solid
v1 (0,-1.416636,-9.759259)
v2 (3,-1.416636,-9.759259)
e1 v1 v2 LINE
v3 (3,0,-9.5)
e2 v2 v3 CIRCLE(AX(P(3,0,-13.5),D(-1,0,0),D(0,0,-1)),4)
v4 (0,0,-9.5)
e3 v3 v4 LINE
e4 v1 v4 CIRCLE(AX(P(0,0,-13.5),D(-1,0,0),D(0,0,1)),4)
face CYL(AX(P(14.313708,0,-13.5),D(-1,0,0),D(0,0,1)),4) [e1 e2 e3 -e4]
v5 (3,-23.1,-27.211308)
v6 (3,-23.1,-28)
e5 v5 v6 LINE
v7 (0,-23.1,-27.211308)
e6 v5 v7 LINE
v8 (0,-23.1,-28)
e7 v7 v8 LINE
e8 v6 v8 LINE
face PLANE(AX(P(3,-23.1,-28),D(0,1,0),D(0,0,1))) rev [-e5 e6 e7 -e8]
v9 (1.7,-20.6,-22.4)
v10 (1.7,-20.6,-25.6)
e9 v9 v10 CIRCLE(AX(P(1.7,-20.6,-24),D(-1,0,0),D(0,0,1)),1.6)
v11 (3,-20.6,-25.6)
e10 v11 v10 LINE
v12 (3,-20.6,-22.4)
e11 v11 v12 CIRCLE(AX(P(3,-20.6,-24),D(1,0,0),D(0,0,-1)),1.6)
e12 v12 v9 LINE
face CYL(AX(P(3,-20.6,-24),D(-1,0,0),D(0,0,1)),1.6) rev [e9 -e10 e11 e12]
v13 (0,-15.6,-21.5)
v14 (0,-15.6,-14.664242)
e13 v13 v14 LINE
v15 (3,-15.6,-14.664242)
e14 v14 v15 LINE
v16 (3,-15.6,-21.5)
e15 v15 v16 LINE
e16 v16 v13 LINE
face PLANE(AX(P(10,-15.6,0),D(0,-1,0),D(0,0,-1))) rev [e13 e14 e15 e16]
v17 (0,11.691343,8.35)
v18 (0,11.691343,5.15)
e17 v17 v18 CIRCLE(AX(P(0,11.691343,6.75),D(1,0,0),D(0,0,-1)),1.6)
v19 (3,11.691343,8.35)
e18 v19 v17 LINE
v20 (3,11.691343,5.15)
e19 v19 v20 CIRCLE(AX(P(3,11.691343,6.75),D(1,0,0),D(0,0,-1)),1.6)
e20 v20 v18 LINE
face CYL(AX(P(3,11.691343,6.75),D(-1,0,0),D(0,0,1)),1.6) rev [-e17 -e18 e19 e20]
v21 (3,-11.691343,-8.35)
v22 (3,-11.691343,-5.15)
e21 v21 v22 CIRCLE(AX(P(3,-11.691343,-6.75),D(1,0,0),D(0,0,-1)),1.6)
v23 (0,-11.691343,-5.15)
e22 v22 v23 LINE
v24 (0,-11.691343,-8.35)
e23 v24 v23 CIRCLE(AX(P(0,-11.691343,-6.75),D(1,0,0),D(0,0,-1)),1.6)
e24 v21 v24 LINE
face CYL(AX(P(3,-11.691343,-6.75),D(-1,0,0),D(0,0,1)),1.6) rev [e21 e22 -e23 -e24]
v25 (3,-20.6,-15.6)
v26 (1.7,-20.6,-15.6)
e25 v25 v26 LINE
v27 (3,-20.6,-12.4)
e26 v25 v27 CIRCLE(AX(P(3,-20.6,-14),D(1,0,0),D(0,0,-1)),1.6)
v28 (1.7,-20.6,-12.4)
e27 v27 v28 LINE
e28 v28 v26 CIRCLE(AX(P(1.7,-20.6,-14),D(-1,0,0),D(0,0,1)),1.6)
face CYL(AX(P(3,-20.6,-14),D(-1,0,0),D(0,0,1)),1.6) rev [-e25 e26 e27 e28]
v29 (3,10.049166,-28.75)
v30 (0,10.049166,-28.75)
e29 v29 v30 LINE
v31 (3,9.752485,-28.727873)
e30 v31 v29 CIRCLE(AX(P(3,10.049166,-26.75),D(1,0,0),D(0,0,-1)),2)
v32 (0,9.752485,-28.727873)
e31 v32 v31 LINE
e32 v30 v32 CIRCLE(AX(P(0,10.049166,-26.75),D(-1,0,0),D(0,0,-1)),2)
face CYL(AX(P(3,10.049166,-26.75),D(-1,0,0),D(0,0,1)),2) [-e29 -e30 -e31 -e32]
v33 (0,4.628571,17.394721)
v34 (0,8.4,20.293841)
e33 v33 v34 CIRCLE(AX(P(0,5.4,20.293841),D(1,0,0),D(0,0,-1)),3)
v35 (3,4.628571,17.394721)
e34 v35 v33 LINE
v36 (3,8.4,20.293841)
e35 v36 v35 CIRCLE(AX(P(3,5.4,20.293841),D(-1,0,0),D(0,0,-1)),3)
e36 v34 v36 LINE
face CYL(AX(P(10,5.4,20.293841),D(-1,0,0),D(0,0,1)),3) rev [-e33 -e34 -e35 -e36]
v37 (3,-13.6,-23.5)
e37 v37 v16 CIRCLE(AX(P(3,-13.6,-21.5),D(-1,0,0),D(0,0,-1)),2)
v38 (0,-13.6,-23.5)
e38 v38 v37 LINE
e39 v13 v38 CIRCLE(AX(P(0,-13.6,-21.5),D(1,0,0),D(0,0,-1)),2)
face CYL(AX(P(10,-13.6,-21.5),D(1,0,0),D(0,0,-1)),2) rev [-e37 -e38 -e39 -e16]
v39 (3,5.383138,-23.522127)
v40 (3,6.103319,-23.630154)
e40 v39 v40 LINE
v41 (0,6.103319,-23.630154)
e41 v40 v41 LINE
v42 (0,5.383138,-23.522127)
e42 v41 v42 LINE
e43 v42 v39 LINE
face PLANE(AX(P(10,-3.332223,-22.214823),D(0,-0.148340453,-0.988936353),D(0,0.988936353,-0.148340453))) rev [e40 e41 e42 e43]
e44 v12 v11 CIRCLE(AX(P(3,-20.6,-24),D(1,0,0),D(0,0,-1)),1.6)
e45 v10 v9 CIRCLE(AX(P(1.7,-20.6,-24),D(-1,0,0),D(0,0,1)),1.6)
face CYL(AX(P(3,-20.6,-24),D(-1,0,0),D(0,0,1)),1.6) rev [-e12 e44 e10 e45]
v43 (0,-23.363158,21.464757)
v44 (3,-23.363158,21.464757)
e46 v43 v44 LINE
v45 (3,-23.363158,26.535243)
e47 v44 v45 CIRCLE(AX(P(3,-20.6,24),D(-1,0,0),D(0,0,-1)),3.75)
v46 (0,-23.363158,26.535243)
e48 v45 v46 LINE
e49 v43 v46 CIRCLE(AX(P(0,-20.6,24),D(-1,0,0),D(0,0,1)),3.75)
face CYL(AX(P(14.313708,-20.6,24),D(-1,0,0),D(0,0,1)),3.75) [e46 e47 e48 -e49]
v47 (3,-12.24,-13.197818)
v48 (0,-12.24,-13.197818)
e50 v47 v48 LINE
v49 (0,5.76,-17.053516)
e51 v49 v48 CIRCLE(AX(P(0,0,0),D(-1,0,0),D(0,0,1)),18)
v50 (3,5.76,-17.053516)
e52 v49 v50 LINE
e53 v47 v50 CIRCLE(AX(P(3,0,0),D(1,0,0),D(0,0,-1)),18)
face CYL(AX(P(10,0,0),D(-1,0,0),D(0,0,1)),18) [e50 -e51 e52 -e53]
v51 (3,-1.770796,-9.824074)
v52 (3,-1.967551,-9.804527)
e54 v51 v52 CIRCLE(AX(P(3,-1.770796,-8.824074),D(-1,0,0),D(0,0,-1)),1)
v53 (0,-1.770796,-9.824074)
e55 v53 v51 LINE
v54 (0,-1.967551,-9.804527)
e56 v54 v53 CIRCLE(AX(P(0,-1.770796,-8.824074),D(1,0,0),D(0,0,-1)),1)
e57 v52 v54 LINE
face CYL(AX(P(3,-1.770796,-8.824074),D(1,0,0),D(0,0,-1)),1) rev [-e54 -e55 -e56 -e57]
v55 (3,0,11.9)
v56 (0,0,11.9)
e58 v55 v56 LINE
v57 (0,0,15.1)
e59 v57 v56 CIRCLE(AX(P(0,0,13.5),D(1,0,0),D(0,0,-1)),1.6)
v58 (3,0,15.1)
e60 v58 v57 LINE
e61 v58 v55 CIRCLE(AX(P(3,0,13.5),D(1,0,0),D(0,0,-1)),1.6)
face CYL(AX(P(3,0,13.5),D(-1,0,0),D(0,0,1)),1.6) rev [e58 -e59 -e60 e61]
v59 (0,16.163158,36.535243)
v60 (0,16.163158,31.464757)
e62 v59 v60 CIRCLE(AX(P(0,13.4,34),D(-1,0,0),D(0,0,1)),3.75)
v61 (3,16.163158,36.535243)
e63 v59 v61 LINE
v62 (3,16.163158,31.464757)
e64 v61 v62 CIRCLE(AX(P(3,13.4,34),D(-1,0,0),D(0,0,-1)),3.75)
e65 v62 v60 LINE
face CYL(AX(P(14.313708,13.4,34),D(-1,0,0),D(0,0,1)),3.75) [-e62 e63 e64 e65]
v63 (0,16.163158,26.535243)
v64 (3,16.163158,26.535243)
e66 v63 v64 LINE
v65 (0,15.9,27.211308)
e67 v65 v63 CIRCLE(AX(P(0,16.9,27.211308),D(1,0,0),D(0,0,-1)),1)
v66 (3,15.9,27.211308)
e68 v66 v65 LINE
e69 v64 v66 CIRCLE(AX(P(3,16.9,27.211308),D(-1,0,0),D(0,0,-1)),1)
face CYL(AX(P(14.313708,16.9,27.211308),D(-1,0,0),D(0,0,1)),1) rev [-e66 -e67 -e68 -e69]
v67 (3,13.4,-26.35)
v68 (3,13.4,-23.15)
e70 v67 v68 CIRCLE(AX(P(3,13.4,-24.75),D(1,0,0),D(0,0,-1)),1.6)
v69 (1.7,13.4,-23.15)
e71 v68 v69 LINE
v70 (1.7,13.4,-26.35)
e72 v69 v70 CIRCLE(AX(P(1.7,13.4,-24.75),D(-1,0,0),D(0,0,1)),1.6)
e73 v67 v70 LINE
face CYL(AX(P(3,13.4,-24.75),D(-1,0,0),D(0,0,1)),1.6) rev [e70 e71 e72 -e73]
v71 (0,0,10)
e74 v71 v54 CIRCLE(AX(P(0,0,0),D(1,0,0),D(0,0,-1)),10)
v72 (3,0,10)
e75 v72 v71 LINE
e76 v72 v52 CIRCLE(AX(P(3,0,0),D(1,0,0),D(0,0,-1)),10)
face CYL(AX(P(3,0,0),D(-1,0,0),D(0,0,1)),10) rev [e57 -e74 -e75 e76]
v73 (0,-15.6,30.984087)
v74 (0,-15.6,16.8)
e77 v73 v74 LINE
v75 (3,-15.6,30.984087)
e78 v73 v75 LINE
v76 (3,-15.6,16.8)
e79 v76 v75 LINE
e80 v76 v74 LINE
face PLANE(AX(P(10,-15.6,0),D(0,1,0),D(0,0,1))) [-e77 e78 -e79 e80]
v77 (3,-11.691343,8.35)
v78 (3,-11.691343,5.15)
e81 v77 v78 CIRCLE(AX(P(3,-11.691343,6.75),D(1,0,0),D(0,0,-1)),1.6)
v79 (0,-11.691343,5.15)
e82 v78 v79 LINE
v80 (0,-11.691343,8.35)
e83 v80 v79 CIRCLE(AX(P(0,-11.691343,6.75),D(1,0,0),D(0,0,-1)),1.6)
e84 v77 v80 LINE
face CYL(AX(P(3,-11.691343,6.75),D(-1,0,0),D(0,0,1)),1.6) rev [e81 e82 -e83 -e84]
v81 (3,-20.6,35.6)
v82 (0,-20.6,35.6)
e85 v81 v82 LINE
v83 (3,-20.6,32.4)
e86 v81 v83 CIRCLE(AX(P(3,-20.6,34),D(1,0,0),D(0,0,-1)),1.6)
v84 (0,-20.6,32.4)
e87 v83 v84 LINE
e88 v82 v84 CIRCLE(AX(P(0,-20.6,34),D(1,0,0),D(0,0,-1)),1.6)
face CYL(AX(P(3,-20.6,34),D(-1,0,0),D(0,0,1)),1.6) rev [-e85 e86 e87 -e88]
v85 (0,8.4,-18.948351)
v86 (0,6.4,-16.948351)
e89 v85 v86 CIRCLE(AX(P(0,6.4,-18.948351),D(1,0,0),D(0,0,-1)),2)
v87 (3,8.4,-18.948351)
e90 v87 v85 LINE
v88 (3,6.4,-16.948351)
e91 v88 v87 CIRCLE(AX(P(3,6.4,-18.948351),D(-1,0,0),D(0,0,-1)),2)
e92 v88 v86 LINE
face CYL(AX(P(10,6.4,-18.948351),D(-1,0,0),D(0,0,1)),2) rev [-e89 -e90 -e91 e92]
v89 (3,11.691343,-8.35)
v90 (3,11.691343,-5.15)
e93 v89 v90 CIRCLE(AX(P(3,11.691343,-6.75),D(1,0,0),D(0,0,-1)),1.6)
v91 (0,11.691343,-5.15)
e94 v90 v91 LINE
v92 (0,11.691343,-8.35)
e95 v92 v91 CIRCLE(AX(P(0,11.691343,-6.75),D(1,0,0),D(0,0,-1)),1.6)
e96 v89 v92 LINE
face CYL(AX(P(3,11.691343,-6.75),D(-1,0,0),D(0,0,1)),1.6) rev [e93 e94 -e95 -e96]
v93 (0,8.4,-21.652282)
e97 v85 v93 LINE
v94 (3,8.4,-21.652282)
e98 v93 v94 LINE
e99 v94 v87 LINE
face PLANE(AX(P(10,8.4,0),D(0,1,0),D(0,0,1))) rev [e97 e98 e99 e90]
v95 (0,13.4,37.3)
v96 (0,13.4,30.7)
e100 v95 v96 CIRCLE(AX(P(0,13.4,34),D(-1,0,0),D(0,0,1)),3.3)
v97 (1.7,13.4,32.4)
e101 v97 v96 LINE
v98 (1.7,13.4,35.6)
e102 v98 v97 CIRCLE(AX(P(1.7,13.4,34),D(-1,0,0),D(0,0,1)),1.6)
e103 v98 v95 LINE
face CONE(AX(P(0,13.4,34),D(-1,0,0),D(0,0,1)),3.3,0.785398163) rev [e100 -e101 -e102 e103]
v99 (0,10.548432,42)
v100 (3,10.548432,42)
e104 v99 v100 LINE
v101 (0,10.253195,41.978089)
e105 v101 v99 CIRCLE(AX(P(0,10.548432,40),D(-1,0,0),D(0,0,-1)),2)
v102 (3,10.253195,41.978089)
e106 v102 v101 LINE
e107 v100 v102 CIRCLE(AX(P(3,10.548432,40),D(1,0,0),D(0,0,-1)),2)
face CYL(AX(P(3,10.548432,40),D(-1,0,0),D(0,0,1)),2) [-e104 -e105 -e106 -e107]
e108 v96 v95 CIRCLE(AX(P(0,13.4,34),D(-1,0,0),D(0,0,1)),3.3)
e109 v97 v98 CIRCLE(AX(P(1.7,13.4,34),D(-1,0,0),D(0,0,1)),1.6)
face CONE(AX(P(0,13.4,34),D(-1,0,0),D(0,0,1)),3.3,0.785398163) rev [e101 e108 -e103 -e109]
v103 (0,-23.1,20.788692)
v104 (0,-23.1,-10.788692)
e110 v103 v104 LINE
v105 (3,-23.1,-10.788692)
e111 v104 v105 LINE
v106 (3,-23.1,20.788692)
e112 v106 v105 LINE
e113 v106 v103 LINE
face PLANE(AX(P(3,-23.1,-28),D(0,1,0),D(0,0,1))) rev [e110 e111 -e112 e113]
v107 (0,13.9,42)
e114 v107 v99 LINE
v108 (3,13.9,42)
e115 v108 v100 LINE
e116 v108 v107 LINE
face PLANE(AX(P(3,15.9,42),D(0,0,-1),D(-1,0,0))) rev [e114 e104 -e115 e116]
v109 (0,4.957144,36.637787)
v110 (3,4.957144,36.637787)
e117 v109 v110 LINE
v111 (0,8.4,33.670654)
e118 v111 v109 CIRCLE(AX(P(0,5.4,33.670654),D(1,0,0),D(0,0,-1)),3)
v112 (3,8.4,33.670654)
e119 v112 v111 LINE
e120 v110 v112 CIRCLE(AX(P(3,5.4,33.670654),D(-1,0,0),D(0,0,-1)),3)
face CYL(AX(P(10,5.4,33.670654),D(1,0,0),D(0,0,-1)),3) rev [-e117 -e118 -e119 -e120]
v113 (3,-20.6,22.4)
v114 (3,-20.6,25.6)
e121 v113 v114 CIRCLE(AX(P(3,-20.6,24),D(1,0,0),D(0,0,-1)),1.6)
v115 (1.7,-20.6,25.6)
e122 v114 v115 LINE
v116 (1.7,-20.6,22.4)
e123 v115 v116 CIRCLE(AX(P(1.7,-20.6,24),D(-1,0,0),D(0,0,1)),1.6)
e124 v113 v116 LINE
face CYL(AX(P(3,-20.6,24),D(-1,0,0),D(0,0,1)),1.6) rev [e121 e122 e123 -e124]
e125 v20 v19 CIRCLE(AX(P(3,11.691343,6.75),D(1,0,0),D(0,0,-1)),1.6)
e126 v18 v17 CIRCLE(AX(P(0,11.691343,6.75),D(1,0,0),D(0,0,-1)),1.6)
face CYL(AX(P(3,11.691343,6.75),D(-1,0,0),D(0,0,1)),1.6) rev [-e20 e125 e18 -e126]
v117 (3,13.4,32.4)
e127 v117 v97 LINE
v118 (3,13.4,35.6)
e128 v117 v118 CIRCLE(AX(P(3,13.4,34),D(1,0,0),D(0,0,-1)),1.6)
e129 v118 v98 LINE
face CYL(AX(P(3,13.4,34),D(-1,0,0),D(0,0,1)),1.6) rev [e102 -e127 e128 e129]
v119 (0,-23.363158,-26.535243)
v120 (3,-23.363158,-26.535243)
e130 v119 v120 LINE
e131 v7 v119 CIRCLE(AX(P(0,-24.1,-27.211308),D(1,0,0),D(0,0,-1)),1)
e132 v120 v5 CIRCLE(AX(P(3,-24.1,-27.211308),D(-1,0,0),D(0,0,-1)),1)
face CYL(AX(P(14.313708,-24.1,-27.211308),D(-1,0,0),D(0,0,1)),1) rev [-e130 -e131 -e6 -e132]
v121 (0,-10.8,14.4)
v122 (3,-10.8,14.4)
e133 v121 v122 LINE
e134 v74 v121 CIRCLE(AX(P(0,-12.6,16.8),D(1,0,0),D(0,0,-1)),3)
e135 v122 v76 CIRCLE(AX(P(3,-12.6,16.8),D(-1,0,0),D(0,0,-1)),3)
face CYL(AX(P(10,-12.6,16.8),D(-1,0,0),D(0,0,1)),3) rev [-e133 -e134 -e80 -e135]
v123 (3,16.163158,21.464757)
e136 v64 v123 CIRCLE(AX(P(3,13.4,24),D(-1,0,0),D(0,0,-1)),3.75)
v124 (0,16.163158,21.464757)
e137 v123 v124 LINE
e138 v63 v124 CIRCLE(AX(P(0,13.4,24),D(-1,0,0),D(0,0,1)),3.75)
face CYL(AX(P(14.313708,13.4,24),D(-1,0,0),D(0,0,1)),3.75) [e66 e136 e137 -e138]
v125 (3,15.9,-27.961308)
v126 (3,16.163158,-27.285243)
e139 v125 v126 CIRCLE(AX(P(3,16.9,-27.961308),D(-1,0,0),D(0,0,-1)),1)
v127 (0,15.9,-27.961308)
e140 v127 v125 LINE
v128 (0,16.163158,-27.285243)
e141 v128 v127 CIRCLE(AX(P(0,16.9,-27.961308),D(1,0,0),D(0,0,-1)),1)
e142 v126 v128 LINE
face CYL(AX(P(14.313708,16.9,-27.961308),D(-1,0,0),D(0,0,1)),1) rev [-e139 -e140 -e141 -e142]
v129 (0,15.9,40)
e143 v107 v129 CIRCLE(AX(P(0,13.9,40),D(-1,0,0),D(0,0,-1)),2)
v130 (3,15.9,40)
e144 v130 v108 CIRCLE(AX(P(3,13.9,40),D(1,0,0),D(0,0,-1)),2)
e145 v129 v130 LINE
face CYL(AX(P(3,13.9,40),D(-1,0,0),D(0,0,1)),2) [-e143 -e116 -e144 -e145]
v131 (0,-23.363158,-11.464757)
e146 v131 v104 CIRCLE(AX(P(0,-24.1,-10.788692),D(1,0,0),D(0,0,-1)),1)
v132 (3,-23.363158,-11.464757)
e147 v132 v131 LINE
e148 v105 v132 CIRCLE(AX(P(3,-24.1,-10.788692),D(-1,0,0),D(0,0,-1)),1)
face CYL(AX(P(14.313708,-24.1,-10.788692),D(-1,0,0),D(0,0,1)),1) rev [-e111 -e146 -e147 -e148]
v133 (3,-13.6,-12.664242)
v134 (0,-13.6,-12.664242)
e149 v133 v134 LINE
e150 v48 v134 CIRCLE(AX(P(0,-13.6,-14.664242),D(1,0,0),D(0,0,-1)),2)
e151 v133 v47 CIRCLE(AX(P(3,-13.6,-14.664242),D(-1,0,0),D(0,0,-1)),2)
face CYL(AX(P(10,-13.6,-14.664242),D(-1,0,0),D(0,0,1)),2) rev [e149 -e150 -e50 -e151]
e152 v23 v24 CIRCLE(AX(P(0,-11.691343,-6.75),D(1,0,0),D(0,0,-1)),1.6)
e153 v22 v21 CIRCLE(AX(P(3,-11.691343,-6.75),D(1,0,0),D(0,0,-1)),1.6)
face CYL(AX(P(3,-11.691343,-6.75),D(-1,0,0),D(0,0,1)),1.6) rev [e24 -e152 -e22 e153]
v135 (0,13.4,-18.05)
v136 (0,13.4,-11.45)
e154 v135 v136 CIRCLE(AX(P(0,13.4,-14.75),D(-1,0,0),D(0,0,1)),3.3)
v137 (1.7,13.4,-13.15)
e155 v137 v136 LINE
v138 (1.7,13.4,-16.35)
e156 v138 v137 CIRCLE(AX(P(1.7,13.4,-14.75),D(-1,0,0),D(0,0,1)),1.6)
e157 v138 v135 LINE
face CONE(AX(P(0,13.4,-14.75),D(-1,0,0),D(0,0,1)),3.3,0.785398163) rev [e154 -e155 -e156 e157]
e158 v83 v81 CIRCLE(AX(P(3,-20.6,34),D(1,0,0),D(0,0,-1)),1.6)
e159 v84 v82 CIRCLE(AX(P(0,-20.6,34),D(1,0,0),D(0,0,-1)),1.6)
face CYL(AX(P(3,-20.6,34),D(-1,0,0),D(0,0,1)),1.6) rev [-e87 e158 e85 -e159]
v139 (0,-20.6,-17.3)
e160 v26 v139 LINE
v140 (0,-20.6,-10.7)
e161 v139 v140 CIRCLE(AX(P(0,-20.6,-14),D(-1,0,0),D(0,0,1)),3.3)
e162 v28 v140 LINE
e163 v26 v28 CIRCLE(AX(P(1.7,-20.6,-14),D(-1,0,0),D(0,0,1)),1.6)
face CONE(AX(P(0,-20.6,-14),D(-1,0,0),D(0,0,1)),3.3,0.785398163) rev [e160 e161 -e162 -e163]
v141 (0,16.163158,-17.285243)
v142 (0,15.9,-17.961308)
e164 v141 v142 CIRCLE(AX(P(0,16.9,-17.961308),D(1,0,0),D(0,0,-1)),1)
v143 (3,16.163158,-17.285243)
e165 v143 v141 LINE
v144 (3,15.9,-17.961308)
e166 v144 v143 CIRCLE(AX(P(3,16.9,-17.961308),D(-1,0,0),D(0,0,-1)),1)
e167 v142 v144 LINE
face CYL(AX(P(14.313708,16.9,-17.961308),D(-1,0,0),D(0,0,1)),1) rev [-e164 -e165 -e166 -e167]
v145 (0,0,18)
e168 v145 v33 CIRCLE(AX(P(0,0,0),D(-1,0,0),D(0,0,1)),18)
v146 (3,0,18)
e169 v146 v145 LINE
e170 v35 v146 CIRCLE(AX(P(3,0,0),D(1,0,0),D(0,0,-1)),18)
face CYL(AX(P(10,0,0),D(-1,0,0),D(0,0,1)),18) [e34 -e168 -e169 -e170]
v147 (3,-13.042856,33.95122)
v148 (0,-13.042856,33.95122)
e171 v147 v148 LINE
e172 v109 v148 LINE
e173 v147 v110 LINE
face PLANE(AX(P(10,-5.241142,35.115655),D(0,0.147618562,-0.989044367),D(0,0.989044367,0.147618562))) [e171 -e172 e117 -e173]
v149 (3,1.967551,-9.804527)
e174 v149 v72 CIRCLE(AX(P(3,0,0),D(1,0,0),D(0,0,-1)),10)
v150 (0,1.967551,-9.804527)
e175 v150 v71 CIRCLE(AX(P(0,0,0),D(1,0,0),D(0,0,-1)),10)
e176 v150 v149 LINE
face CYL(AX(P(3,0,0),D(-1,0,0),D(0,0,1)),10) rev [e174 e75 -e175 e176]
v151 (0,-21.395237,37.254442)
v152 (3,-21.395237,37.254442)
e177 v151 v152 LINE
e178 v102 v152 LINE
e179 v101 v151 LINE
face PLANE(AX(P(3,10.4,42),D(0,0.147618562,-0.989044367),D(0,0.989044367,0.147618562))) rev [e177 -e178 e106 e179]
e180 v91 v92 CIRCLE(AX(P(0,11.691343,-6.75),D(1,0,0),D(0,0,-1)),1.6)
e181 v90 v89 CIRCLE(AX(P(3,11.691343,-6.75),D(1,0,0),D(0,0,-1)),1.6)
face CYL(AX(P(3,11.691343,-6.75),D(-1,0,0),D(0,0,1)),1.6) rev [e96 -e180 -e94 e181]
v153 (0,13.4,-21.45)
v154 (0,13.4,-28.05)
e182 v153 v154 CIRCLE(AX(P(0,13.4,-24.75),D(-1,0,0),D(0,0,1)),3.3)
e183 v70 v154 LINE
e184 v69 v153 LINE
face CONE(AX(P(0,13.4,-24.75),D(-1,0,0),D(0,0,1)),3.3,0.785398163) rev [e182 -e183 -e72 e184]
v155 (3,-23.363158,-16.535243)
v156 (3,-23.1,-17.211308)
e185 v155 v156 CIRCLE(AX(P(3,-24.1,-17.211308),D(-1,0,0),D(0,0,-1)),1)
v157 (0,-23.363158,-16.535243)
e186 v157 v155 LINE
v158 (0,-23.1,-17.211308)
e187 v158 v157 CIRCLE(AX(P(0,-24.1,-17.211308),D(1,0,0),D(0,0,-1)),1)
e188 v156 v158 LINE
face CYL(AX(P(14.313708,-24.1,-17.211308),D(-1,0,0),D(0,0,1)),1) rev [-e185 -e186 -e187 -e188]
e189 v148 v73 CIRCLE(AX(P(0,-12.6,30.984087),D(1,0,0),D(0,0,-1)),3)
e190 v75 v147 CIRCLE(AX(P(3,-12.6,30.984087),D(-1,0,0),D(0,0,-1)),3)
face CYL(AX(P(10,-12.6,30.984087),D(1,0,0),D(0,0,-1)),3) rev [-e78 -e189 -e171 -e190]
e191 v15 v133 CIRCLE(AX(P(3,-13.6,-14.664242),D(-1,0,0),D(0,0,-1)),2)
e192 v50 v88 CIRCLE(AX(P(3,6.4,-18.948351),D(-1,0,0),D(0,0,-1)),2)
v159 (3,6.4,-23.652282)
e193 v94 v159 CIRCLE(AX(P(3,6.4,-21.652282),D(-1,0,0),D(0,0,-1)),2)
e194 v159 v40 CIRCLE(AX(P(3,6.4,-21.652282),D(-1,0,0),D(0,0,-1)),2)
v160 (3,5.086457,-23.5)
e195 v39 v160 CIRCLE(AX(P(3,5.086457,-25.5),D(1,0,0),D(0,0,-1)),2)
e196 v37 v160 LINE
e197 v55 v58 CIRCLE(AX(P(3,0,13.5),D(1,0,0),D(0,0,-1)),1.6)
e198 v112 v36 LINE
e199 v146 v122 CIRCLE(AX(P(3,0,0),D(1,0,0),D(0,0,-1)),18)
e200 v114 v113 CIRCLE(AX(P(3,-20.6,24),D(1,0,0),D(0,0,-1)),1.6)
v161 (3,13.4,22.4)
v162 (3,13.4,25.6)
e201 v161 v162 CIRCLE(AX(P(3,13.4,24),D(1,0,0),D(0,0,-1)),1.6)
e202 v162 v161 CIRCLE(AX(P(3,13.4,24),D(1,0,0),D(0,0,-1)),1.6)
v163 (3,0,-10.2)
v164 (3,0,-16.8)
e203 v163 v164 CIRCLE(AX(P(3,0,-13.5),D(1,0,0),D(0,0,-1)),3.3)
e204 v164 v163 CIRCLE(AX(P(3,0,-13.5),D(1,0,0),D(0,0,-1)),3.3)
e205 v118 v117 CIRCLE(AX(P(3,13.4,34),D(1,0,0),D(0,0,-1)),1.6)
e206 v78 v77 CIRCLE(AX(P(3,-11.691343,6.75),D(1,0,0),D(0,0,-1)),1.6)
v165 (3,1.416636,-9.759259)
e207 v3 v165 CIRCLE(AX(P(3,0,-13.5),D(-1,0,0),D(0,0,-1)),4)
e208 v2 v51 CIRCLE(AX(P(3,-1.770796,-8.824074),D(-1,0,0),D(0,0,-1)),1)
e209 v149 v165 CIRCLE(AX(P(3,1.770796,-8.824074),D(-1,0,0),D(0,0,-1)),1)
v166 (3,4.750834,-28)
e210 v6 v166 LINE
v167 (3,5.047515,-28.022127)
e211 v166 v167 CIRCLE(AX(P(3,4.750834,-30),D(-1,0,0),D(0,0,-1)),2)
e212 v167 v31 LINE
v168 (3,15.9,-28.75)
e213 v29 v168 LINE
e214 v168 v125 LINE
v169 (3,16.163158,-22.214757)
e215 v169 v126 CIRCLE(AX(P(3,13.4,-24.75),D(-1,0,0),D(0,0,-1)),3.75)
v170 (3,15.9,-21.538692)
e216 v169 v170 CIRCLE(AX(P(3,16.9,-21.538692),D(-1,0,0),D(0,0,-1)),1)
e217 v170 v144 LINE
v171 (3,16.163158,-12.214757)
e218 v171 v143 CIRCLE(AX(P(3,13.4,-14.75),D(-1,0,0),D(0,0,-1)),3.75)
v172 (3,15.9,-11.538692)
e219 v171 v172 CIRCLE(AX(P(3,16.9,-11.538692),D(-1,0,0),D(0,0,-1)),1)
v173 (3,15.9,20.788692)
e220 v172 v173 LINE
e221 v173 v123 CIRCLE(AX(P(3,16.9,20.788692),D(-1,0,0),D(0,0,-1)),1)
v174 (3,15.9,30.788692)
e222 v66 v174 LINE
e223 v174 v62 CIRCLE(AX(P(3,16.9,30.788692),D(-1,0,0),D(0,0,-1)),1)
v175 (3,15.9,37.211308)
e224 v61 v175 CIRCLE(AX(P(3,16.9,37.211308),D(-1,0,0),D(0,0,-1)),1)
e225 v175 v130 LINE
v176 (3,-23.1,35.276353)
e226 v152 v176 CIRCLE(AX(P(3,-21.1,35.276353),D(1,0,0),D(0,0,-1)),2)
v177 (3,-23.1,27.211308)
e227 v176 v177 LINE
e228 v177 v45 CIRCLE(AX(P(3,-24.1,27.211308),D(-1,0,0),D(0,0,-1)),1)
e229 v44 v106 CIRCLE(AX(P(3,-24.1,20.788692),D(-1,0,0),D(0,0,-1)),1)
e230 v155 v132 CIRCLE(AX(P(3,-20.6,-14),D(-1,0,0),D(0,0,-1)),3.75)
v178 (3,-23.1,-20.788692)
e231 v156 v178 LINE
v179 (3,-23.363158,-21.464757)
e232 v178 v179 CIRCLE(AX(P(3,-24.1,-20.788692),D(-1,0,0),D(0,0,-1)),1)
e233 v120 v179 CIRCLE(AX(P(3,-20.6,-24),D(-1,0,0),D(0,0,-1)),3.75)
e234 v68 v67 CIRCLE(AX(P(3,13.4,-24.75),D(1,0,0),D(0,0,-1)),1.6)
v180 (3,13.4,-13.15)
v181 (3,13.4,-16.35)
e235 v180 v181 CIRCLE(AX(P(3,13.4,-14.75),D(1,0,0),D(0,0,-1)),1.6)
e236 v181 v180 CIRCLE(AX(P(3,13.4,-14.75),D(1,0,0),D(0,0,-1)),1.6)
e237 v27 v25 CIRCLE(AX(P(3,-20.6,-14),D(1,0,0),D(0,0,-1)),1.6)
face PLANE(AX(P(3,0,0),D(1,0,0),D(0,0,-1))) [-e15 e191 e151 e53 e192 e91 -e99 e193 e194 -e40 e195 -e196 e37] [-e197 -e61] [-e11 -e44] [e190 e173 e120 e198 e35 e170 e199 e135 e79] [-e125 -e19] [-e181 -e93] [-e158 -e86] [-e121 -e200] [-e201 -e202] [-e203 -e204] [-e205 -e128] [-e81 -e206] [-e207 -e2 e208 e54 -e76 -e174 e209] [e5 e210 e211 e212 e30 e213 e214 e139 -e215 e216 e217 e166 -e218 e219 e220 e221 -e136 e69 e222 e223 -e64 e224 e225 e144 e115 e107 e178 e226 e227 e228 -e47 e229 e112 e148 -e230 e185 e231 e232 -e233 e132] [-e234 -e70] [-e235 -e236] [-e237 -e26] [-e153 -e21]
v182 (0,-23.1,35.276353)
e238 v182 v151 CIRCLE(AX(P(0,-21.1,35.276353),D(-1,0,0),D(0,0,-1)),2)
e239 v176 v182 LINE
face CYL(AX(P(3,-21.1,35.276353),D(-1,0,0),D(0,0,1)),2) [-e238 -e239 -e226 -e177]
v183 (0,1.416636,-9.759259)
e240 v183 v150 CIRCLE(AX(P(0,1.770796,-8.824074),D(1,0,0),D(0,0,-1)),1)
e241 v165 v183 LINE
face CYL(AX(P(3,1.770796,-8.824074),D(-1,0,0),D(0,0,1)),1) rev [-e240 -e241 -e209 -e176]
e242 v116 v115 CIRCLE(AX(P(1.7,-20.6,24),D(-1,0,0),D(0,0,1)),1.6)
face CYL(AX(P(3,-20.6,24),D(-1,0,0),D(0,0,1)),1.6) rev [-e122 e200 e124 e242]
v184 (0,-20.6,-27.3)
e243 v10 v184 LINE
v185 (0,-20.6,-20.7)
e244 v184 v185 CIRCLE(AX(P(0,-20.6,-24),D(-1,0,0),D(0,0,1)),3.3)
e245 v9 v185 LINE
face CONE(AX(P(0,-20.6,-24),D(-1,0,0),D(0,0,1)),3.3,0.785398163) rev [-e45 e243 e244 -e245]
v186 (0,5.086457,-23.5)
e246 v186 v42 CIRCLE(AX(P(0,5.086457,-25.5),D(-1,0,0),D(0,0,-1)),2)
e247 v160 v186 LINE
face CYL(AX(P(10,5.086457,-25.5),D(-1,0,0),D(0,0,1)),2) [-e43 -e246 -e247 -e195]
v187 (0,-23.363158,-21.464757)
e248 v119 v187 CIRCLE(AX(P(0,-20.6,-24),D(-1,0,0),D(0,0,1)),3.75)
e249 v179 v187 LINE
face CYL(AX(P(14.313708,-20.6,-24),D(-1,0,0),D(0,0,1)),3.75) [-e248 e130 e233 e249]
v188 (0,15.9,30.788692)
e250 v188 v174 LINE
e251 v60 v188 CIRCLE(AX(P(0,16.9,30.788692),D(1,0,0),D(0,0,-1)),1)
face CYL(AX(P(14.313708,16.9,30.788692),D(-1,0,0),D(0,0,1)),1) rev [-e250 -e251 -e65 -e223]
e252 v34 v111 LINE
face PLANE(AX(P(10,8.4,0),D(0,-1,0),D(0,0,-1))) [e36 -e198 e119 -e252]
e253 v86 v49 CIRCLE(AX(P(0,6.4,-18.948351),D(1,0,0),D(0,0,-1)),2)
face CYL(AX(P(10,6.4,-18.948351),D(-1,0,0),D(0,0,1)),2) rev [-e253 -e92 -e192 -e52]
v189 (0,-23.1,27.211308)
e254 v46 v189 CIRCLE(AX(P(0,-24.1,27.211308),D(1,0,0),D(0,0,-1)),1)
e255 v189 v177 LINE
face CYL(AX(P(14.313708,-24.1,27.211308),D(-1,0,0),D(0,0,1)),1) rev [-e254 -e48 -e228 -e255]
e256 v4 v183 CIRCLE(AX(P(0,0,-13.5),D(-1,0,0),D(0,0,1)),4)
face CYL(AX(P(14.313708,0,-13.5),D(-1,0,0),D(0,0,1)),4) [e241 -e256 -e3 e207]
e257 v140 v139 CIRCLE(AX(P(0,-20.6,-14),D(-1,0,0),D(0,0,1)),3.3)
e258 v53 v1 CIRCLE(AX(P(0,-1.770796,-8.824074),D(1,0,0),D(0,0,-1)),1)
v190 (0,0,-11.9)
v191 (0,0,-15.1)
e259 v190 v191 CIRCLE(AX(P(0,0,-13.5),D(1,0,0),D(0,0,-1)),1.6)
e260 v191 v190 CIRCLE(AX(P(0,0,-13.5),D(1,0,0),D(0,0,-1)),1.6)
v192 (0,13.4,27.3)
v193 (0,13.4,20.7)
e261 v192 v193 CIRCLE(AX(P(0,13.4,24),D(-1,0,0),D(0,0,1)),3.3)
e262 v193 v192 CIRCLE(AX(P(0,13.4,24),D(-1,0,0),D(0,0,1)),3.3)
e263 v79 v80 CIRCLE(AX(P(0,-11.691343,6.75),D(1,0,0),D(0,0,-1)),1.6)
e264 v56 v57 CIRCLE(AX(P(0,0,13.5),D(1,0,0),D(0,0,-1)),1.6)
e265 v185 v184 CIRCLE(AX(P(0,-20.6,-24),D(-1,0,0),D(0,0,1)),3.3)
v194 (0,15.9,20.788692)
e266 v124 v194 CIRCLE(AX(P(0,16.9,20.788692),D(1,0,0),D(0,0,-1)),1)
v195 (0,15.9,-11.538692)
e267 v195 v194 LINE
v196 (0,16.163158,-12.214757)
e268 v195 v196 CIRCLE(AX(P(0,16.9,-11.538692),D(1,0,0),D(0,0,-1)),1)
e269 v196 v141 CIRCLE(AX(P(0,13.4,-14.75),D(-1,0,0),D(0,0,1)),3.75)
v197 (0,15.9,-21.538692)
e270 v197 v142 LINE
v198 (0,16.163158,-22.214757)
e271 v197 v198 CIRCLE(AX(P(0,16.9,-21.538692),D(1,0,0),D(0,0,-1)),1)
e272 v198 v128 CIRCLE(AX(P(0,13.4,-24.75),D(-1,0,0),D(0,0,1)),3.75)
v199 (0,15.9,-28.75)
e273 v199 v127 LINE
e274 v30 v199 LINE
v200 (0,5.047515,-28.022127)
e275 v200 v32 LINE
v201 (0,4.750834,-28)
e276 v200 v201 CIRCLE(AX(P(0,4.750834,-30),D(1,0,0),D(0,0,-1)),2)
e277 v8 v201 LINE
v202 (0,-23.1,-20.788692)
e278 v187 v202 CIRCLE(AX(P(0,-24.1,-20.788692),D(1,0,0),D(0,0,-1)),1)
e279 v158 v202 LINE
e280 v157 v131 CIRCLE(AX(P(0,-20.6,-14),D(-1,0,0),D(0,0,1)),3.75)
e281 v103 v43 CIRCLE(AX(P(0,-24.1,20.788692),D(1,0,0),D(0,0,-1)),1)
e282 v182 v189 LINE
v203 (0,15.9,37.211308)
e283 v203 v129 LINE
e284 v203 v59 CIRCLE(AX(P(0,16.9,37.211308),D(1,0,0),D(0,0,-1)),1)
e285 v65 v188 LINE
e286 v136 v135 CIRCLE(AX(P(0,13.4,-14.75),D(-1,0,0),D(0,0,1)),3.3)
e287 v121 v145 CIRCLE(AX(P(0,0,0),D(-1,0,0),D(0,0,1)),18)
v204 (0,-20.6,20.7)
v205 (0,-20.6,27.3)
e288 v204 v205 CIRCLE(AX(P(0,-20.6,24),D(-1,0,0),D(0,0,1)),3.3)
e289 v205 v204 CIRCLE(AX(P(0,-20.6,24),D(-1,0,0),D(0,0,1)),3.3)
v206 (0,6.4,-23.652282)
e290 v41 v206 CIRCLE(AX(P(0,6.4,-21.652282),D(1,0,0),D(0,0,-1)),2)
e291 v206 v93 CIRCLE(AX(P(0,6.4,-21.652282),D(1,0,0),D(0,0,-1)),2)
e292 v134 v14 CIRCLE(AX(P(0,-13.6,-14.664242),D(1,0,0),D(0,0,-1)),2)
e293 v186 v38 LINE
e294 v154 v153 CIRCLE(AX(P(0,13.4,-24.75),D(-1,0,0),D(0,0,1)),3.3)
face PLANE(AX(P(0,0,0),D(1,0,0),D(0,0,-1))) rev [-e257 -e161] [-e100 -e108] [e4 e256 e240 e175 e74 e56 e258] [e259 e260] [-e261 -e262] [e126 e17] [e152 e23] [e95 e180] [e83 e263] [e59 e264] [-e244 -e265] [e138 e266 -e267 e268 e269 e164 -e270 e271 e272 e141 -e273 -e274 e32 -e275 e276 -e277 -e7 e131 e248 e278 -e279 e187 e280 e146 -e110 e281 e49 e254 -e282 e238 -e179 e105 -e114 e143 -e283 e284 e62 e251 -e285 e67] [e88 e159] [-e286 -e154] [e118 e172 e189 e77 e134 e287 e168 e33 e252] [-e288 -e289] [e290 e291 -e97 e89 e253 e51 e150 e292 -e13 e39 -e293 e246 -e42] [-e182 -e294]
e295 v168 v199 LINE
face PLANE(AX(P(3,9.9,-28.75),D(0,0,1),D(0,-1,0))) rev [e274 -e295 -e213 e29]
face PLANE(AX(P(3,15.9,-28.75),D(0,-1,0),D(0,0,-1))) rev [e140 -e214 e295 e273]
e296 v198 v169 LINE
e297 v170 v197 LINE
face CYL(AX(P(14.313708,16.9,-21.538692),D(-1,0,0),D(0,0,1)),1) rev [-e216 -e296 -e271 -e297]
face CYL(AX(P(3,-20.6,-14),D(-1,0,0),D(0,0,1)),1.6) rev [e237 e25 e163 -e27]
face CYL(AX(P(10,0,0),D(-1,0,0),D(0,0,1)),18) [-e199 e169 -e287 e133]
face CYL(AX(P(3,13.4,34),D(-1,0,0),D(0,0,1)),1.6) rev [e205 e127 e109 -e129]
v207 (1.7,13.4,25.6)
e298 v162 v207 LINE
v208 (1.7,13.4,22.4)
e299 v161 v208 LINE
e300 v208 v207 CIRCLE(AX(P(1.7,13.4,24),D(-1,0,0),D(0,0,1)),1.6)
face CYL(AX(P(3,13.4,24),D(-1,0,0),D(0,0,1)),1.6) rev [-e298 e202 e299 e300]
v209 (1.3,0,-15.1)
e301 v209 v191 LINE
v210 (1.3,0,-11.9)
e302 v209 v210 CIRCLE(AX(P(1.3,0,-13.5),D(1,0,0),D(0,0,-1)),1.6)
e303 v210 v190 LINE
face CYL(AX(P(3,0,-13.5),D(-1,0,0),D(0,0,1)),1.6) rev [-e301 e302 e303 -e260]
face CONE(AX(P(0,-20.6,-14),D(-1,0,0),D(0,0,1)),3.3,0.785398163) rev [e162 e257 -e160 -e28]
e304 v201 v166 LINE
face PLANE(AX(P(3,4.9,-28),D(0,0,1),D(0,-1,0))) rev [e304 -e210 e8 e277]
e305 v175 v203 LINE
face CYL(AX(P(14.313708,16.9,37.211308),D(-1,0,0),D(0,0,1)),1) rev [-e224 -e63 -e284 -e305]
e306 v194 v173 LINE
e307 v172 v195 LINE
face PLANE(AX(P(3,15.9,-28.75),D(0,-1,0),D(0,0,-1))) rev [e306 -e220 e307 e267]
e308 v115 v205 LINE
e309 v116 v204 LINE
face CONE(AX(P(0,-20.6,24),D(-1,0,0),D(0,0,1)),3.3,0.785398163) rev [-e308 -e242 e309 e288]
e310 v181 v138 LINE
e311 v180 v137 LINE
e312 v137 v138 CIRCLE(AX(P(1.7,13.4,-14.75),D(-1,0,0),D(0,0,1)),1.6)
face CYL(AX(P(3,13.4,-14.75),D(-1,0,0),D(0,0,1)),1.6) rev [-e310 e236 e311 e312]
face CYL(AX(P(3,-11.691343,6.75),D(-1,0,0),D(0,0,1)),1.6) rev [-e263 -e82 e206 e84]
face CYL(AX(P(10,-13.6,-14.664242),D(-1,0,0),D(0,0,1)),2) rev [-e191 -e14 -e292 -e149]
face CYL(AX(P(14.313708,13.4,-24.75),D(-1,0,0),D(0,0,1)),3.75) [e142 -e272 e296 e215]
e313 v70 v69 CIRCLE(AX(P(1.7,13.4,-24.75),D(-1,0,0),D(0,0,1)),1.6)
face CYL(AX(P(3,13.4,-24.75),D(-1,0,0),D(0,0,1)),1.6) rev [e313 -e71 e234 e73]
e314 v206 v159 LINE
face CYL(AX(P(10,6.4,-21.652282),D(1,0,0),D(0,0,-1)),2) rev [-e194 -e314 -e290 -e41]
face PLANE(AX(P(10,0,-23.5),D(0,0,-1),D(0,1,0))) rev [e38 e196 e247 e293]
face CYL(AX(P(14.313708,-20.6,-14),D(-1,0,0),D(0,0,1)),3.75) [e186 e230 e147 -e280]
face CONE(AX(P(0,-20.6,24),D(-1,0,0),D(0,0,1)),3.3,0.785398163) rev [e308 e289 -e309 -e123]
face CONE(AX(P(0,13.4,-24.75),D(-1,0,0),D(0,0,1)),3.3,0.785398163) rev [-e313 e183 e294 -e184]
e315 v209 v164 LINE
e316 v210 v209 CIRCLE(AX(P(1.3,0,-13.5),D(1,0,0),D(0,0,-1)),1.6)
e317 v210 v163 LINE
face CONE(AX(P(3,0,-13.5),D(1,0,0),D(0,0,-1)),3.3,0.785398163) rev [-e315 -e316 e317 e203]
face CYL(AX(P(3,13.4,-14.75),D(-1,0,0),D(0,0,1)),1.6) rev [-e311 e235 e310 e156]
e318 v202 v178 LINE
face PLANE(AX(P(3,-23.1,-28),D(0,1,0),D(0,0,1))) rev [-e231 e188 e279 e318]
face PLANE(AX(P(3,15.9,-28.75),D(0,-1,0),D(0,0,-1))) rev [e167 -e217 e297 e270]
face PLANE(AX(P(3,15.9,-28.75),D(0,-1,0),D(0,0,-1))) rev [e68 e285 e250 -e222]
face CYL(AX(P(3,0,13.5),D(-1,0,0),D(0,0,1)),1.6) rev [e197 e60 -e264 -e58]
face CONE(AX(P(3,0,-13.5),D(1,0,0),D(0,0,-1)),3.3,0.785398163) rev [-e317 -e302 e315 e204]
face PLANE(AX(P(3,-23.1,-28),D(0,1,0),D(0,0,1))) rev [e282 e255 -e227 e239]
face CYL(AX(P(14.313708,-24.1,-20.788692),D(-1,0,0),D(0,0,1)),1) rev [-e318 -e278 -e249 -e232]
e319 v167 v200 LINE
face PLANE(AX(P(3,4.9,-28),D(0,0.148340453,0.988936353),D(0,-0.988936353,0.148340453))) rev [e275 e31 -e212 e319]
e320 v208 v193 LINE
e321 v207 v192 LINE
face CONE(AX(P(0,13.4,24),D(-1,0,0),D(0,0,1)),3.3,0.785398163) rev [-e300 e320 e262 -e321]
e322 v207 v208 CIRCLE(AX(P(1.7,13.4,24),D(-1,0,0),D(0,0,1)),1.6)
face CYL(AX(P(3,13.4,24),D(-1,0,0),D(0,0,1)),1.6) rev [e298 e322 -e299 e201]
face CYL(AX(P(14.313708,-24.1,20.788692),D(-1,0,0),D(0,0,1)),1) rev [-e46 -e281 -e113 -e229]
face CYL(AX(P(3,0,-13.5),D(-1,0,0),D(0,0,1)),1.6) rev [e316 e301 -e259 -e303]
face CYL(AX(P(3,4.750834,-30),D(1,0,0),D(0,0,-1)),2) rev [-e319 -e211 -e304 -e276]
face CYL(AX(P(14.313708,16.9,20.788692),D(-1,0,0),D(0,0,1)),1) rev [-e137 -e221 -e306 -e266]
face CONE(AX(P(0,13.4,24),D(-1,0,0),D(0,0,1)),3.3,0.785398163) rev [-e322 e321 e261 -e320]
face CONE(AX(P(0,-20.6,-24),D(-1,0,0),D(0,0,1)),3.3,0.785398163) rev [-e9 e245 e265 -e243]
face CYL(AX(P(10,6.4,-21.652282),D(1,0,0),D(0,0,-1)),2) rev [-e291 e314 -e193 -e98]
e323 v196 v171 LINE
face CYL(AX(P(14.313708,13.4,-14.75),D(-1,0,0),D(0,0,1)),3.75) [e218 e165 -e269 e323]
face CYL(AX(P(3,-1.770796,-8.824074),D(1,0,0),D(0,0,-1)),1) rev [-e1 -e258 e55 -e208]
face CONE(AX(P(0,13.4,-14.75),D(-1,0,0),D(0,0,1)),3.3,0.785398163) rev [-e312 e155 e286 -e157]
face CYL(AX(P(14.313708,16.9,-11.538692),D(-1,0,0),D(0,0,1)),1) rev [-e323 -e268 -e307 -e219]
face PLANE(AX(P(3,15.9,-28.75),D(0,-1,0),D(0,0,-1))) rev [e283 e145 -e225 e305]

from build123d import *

# Parameters (mm, degrees)
SKETCH_1_R                   = 1.6
SKETCH_1_R_2                 = 10
EXTRUDE_1_DEPTH              = 3
SKETCH_2_R                   = 3.75
SKETCH_2_R_2                 = 1.6
SKETCH_2_R_3                 = 4
EXTRUDE_2_DEPTH              = 3
HOLE_WIZARD_M3_1_D           = 3.2
HOLE_WIZARD_M3_1_DEPTH       = 7.5
HOLE_WIZARD_M3_1_CSINK_D     = 6.6
HOLE_WIZARD_M3_1_CSINK_ANGLE = 90
HOLE_WIZARD_M3_1_TIP         = 0.96137699
CUT_EXTRUDE_1_DEPTH          = 10
HOLE_WIZARD_M3_2_D           = 3.2
HOLE_WIZARD_M3_2_DEPTH       = 7.5
HOLE_WIZARD_M3_2_CSINK_D     = 6.6
HOLE_WIZARD_M3_2_CSINK_ANGLE = 90
HOLE_WIZARD_M3_2_TIP         = 0.96137699
FILLET_1_R                   = 3
FILLET_2_R                   = 2
FILLET_3_R                   = 1


with BuildPart() as part:
    # 草图1 → 凸台-拉伸1 (new body)
    with BuildSketch(Plane(origin=(0, 0, 0), x_dir=(0, 0, -1), z_dir=(1, 0, 0))):
        Polygon((28, 4.9), (28, -23.1), (-37, -23.1), (-42, 10.4), (-42, 15.9), (28.75, 15.9), (28.75, 9.9), align=None)
        with Locations((-13.5, 0)):
            Circle(SKETCH_1_R, mode=Mode.SUBTRACT)
        with Locations((-6.75, 11.691342951)):
            Circle(SKETCH_1_R, mode=Mode.SUBTRACT)
        with Locations((6.75, 11.691342951)):
            Circle(SKETCH_1_R, mode=Mode.SUBTRACT)
        with Locations((13.5, 0)):
            Circle(SKETCH_1_R, mode=Mode.SUBTRACT)
        with Locations((6.75, -11.691342951)):
            Circle(SKETCH_1_R, mode=Mode.SUBTRACT)
        with Locations((-6.75, -11.691342951)):
            Circle(SKETCH_1_R, mode=Mode.SUBTRACT)
        Circle(SKETCH_1_R_2, mode=Mode.SUBTRACT)
        with Locations((14, -20.6)):
            Circle(SKETCH_1_R, mode=Mode.SUBTRACT)
        with Locations((24, -20.6)):
            Circle(SKETCH_1_R, mode=Mode.SUBTRACT)
        with Locations((24.75, 13.4)):
            Circle(SKETCH_1_R, mode=Mode.SUBTRACT)
        with Locations((14.75, 13.4)):
            Circle(SKETCH_1_R, mode=Mode.SUBTRACT)
        with Locations((-24, -20.6)):
            Circle(SKETCH_1_R, mode=Mode.SUBTRACT)
        with Locations((-34, -20.6)):
            Circle(SKETCH_1_R, mode=Mode.SUBTRACT)
        with Locations((-34, 13.4)):
            Circle(SKETCH_1_R, mode=Mode.SUBTRACT)
        with Locations((-24, 13.4)):
            Circle(SKETCH_1_R, mode=Mode.SUBTRACT)
    extrude(amount=EXTRUDE_1_DEPTH)

    # 草图2 → 凸台-拉伸2 (add)
    # profile 1 of 8: a face of its own
    with BuildSketch(Plane.ZY):
        with Locations((-24.75, 13.4)):
            Circle(SKETCH_2_R)
        with Locations(Location((-24.75, 13.4, 0), (0, 0, 180))):
            Circle(SKETCH_2_R_2, mode=Mode.SUBTRACT)
    # profile 2 of 8: a face of its own
    with BuildSketch(Plane.ZY):
        with Locations((-14.75, 13.4)):
            Circle(SKETCH_2_R)
        with Locations(Location((-14.75, 13.4, 0), (0, 0, 180))):
            Circle(SKETCH_2_R_2, mode=Mode.SUBTRACT)
    # profile 3 of 8: a face of its own
    with BuildSketch(Plane.ZY):
        with Locations((24, 13.4)):
            Circle(SKETCH_2_R)
        with Locations(Location((24, 13.4, 0), (0, 0, 180))):
            Circle(SKETCH_2_R_2, mode=Mode.SUBTRACT)
    # profile 4 of 8: a face of its own
    with BuildSketch(Plane.ZY):
        with Locations((24, -20.6)):
            Circle(SKETCH_2_R)
        with Locations(Location((24, -20.6, 0), (0, 0, 180))):
            Circle(SKETCH_2_R_2, mode=Mode.SUBTRACT)
    # profile 5 of 8: a face of its own
    with BuildSketch(Plane.ZY):
        with Locations((-24, -20.6)):
            Circle(SKETCH_2_R)
        with Locations(Location((-24, -20.6, 0), (0, 0, 180))):
            Circle(SKETCH_2_R_2, mode=Mode.SUBTRACT)
    # profile 6 of 8: a face of its own
    with BuildSketch(Plane.ZY):
        with Locations((-14, -20.6)):
            Circle(SKETCH_2_R)
        with Locations(Location((-14, -20.6, 0), (0, 0, 180))):
            Circle(SKETCH_2_R_2, mode=Mode.SUBTRACT)
    # profile 7 of 8: a face of its own
    with BuildSketch(Plane.ZY):
        with Locations((-13.5, 0)):
            Circle(SKETCH_2_R_3)
        with Locations(Location((-13.5, 0, 0), (0, 0, 180))):
            Circle(SKETCH_2_R_2, mode=Mode.SUBTRACT)
    # profile 8 of 8: a face of its own
    with BuildSketch(Plane.ZY):
        with Locations((34, 13.4)):
            Circle(SKETCH_2_R)
        with Locations(Location((34, 13.4, 0), (0, 0, 180))):
            Circle(SKETCH_2_R_2, mode=Mode.SUBTRACT)
    extrude(amount=-EXTRUDE_2_DEPTH)

    # M3 十字槽半沉头木螺钉的锥形沉头孔1
    with Locations(Plane.ZY):
        with Locations((-24.75, 13.4), (-14.75, 13.4), (-24, -20.6), (-14, -20.6), (24, 13.4), (34, 13.4), (24, -20.6)):
            CounterSinkHole(HOLE_WIZARD_M3_1_D / 2, HOLE_WIZARD_M3_1_CSINK_D / 2, depth=HOLE_WIZARD_M3_1_DEPTH, counter_sink_angle=HOLE_WIZARD_M3_1_CSINK_ANGLE)
            with Locations((0, 0, -(HOLE_WIZARD_M3_1_DEPTH + HOLE_WIZARD_M3_1_TIP / 2))):  # 118° drill point
                Cone(0, HOLE_WIZARD_M3_1_D / 2, HOLE_WIZARD_M3_1_TIP, mode=Mode.SUBTRACT)

    # 草图17 → 切除-拉伸1 (cut)
    with BuildSketch(Plane.ZY):
        with BuildLine():
            Line((37.15164609, 8.4), (15.919798994, 8.4))
            ThreePointArc((15.919798994, 8.4), (17.472211965, 4.326870585), (18, 0))
            ThreePointArc((18, 0), (15.582676264, -9.010005574), (8.979977728, -15.6))
            Line((8.979977728, -15.6), (33.569556538, -15.6))
            Line((33.569556538, -15.6), (37.15164609, 8.4))
        make_face()
        with BuildLine():
            ThreePointArc((-8.979977728, -15.6), (-17.291608375, -5.00002798), (-15.919798994, 8.4))
            Line((-15.919798994, 8.4), (-23.974656606, 8.4))
            Line((-23.974656606, 8.4), (-23.5, 5.235622624))
            Line((-23.5, 5.235622624), (-23.5, -15.6))
            Line((-23.5, -15.6), (-8.979977728, -15.6))
        make_face()
    extrude(amount=-CUT_EXTRUDE_1_DEPTH, mode=Mode.SUBTRACT)

    # M3 十字槽半沉头木螺钉的锥形沉头孔2
    with Locations(Plane(origin=(3, 0, 0), x_dir=(0, 0, -1), z_dir=(1, 0, 0))):
        with Locations((13.5, 0)):
            CounterSinkHole(HOLE_WIZARD_M3_2_D / 2, HOLE_WIZARD_M3_2_CSINK_D / 2, depth=HOLE_WIZARD_M3_2_DEPTH, counter_sink_angle=HOLE_WIZARD_M3_2_CSINK_ANGLE)
            with Locations((0, 0, -(HOLE_WIZARD_M3_2_DEPTH + HOLE_WIZARD_M3_2_TIP / 2))):  # 118° drill point
                Cone(0, HOLE_WIZARD_M3_2_D / 2, HOLE_WIZARD_M3_2_TIP, mode=Mode.SUBTRACT)

    # 圆角1
    fillet_1_edges = [part.edges().sort_by_distance(p)[0] for p in [
        (1.5, -15.6, 8.979977728),
        (1.5, 8.4, 15.919798994),
        (1.5, 8.4, 37.15164609),
        (1.5, -15.6, 33.569556538),
    ]]
    fillet(fillet_1_edges, radius=FILLET_1_R)

    # 圆角2
    fillet_2_edges = [part.edges().sort_by_distance(p)[0] for p in [
        (1.5, 9.9, -28.75),
        (1.5, 4.9, -28),
        (1.5, -23.1, 37),
        (1.5, 10.4, 42),
        (1.5, 15.9, 42),
        (1.5, 8.4, -15.919798994),
        (1.5, -15.6, -8.979977728),
        (1.5, -15.6, -23.5),
        (1.5, 5.235622624, -23.5),
        (1.5, 8.4, -23.974656606),
    ]]
    fillet(fillet_2_edges, radius=FILLET_2_R)

    # 圆角3
    fillet_3_edges = [part.edges().sort_by_distance(p)[0] for p in [
        (1.5, 15.9, -11.954915028),
        (1.5, 15.9, -17.545084972),
        (1.5, 15.9, 26.795084972),
        (1.5, 15.9, 21.204915028),
        (1.5, -23.1, 26.795084972),
        (1.5, -23.1, 21.204915028),
        (1.5, -23.1, -26.795084972),
        (1.5, -23.1, -21.204915028),
        (1.5, -23.1, -16.795084972),
        (1.5, -23.1, -11.204915028),
        (1.5, 1.660869548, -9.861111111),
        (1.5, -1.660869548, -9.861111111),
        (1.5, 15.9, 36.795084972),
        (1.5, 15.9, 31.204915028),
        (1.5, 15.9, -27.545084972),
        (1.5, 15.9, -21.954915028),
    ]]
    fillet(fillet_3_edges, radius=FILLET_3_R)


solid = part.part
